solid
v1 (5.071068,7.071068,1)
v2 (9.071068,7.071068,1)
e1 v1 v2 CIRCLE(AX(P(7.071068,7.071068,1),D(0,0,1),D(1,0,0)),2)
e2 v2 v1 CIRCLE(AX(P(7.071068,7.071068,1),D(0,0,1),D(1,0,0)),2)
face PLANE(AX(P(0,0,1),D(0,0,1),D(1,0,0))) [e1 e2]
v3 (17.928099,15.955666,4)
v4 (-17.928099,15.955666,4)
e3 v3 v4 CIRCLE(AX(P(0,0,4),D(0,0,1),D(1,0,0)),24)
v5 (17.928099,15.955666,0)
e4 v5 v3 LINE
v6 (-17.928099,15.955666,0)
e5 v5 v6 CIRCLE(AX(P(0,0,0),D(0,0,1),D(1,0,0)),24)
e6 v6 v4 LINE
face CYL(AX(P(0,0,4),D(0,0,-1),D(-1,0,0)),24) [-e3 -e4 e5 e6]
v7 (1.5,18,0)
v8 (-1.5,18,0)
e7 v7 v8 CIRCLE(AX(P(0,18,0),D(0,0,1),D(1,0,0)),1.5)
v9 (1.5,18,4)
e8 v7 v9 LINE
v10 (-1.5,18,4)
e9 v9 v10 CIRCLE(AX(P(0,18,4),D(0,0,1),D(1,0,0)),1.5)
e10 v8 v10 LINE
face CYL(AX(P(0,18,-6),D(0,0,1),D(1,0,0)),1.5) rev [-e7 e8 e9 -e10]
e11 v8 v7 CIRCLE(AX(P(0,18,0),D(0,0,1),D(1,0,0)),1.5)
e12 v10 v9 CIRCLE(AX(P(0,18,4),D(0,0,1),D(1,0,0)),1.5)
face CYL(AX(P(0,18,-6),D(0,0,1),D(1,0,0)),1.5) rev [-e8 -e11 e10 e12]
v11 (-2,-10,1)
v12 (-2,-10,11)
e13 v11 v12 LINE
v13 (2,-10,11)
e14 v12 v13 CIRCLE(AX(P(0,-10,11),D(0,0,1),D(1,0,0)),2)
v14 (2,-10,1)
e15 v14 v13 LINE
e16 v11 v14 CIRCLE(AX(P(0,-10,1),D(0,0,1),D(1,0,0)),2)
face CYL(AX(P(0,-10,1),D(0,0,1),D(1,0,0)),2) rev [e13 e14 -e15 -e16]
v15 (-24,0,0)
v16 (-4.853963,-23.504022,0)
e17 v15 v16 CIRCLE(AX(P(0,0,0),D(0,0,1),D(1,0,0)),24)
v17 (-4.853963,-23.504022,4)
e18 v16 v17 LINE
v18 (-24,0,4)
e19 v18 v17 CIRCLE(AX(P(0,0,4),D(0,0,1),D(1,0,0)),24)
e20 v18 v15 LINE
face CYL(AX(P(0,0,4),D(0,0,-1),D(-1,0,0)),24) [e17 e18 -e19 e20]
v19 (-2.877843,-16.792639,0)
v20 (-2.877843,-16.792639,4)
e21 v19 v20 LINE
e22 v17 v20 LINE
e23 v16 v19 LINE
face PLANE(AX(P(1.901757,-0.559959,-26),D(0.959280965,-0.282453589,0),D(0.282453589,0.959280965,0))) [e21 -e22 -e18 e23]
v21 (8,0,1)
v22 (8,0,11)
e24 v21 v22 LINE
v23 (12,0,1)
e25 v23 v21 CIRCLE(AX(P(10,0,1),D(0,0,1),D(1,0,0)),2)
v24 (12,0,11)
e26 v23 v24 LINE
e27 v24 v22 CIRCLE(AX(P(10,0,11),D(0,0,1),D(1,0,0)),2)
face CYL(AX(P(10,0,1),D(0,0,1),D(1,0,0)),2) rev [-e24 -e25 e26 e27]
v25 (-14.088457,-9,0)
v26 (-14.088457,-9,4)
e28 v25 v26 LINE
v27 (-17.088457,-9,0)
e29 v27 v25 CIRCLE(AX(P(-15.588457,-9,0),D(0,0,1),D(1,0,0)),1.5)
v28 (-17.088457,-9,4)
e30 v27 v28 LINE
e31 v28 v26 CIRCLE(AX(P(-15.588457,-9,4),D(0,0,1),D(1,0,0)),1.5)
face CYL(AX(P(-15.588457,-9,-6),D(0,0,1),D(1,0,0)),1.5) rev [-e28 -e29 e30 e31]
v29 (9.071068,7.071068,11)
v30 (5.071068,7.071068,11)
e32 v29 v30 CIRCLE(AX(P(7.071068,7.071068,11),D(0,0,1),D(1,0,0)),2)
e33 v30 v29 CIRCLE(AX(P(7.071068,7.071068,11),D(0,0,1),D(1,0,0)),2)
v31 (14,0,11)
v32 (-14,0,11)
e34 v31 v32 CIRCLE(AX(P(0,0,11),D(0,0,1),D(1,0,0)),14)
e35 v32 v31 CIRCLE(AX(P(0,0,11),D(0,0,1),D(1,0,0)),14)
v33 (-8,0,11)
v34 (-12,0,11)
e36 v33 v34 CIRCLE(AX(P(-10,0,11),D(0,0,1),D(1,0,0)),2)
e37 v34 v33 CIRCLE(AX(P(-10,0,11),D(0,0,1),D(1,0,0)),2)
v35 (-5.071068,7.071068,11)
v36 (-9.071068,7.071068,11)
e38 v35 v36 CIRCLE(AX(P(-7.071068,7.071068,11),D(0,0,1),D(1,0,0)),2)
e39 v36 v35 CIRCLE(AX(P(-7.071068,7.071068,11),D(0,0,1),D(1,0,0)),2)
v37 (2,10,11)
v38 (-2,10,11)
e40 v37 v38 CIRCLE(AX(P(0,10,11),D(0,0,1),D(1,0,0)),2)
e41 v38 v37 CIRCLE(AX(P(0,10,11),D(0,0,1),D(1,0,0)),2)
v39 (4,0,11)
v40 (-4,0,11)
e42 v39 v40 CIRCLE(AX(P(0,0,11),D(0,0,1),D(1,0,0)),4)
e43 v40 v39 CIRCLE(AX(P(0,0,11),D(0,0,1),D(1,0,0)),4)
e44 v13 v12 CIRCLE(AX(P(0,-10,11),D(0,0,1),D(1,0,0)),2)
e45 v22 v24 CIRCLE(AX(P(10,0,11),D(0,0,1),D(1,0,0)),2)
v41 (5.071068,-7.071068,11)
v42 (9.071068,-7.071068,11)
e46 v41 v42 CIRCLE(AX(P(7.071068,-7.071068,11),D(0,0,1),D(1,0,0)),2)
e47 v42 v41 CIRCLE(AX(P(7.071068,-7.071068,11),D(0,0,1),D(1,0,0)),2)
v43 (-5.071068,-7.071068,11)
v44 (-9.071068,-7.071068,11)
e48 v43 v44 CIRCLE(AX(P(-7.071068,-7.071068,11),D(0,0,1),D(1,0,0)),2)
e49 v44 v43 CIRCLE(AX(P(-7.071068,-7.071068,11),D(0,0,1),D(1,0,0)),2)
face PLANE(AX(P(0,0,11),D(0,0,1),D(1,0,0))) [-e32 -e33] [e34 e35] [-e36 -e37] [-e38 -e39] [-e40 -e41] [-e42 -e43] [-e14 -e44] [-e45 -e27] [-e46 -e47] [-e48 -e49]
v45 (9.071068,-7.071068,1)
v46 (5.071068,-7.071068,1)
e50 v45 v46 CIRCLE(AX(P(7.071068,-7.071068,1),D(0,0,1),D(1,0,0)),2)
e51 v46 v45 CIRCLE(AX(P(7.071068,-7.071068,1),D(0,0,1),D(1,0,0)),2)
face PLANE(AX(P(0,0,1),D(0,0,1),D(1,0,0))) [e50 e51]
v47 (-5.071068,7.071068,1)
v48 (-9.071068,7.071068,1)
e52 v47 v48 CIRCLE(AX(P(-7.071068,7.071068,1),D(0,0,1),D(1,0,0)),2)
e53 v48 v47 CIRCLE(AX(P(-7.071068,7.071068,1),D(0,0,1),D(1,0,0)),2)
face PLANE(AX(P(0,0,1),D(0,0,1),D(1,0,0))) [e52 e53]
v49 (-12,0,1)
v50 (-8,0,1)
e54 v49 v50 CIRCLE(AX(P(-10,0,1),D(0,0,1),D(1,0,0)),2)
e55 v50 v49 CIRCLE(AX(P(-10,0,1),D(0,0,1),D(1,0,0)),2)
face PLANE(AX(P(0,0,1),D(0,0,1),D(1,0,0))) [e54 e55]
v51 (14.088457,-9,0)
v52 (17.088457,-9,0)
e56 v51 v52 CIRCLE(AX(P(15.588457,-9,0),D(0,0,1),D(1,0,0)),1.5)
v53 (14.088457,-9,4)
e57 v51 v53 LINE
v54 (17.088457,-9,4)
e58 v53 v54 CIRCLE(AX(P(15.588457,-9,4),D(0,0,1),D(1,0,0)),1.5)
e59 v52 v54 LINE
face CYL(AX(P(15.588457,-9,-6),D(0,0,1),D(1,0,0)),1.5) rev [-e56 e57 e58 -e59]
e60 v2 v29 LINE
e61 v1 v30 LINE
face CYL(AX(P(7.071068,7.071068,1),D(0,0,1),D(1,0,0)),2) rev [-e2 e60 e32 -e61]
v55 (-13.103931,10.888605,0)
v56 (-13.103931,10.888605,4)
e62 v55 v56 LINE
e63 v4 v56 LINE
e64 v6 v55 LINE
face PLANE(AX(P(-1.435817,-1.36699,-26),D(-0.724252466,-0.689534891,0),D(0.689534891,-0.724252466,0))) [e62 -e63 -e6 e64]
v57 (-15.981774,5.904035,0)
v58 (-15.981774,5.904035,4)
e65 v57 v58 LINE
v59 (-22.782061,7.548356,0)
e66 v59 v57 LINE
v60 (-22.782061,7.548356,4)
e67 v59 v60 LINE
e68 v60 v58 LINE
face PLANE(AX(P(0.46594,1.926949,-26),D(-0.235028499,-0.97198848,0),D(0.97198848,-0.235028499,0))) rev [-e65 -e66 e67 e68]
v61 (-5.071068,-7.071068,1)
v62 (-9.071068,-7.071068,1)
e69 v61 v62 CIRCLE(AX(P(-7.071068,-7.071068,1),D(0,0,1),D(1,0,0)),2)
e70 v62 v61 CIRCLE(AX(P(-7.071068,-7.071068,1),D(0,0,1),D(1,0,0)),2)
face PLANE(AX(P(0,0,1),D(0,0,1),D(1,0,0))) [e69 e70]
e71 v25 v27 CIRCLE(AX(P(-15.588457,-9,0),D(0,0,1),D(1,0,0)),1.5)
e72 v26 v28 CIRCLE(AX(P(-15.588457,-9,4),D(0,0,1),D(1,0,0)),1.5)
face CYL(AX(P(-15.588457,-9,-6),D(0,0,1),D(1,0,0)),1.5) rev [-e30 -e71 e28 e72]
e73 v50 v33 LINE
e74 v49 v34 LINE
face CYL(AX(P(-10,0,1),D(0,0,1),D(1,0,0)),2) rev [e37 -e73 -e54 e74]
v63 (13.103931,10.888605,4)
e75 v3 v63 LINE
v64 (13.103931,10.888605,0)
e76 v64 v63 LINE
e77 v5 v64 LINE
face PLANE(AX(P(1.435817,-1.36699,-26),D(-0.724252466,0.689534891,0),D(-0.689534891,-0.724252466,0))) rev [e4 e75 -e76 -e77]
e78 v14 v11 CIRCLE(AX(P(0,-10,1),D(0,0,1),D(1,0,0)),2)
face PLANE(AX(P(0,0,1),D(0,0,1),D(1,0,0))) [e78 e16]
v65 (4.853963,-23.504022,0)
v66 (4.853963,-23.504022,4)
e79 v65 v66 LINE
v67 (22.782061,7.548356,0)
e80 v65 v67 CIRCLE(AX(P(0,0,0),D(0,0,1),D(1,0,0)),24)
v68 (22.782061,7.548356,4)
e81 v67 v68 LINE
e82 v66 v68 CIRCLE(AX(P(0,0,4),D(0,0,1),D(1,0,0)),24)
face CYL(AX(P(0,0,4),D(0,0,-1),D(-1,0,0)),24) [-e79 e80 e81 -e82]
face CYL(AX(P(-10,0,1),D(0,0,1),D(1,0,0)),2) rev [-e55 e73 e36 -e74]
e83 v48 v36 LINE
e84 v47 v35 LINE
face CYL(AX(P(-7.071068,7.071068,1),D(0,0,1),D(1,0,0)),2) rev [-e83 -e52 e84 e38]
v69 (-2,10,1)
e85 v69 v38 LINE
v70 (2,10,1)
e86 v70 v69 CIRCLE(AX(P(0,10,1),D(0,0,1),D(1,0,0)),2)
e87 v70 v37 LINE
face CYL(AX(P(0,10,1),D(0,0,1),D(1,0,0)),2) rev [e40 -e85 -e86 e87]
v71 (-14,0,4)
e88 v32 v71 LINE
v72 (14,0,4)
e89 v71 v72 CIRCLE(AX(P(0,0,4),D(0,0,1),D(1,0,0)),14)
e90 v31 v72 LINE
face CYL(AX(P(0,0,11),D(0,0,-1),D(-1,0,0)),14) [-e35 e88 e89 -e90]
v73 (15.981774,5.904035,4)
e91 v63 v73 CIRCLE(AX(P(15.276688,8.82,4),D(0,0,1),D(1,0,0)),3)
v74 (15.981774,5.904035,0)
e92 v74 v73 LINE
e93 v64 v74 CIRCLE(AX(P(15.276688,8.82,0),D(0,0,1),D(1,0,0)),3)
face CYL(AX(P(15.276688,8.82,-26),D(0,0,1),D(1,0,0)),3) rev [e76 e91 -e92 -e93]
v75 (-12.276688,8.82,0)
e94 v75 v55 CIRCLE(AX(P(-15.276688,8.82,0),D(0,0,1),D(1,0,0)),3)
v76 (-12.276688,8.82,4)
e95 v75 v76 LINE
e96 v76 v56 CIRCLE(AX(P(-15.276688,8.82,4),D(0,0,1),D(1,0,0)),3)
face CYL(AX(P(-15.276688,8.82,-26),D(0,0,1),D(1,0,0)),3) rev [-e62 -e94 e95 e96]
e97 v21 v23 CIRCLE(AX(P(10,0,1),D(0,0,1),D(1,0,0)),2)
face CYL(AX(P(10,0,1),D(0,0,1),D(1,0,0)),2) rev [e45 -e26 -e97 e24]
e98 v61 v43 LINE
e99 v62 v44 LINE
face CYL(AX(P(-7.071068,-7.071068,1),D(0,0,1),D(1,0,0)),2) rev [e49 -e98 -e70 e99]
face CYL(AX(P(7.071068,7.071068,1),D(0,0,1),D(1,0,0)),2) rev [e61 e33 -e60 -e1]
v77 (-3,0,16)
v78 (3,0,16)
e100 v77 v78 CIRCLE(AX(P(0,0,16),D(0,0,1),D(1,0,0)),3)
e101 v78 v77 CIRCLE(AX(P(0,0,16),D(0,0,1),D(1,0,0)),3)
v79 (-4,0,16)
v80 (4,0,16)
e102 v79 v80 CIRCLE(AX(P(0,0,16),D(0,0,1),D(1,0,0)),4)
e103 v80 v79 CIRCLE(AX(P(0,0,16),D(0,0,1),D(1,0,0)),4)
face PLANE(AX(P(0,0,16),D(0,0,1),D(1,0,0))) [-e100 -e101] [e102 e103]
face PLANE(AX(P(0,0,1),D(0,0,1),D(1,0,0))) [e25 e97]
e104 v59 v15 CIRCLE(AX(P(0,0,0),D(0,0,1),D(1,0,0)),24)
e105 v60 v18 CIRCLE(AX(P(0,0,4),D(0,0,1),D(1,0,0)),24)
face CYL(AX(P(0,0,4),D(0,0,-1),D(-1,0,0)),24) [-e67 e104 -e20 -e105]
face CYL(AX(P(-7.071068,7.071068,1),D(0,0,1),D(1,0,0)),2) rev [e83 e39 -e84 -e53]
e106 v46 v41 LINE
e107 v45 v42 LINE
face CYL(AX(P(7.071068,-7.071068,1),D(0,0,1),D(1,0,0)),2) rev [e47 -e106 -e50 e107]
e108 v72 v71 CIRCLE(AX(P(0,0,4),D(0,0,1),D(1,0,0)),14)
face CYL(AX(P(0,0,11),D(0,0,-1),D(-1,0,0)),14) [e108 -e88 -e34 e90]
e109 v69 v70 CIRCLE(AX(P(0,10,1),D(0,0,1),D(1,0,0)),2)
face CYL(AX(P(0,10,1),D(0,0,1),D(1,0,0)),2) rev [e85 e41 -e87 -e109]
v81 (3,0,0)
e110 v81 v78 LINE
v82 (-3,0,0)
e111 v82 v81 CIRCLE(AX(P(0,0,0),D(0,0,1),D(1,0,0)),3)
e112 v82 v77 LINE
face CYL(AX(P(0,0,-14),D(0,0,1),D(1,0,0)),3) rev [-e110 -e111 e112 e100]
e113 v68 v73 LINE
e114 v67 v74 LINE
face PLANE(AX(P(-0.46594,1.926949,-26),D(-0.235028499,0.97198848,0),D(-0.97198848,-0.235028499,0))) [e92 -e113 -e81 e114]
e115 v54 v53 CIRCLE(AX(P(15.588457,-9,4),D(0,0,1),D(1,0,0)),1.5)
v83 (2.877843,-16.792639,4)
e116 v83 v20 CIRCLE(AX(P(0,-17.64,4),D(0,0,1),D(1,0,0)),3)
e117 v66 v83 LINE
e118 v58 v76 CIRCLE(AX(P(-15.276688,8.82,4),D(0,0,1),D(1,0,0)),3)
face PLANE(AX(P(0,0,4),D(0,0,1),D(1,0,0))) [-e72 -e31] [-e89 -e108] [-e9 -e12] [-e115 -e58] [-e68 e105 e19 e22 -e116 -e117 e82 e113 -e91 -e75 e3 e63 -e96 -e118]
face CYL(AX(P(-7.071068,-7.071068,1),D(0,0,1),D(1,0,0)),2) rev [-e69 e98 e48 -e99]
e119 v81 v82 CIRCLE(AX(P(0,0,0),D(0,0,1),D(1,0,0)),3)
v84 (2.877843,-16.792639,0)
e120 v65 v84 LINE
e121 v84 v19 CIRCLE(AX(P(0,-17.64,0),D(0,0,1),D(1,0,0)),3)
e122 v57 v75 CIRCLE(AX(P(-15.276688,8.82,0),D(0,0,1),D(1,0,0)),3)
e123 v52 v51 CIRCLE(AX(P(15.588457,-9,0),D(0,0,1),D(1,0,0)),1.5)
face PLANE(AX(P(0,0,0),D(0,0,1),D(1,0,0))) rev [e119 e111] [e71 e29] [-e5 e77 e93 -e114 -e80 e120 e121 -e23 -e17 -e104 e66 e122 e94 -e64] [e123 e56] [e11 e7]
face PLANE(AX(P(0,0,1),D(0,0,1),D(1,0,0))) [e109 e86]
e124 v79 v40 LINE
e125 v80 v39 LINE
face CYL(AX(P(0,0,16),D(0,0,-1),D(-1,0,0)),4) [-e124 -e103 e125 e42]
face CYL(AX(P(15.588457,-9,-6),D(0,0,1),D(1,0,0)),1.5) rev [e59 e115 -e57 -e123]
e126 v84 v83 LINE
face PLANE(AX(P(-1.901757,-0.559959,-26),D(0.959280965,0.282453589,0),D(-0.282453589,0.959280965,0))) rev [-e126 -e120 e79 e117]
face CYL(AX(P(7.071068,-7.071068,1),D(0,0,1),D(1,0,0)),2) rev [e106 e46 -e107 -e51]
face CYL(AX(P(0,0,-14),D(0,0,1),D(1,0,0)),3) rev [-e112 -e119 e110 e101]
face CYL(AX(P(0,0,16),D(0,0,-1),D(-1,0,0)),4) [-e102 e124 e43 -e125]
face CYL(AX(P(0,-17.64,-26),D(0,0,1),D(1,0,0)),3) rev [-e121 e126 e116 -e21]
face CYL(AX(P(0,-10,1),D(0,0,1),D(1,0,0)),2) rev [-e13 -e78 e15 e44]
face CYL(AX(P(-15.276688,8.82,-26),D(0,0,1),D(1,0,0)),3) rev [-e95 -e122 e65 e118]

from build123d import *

# Parameters (mm, degrees)
FLANGE_DISC_SKETCH_R    = 24
FLANGE_DISC_48_DEPTH    = 4
HUB_SKETCH_R            = 14
HUB_28_DEPTH            = 7
FLANGE_HOLES_SKETCH_R   = 1.5
FLANGE_HOLES_3X_3_DEPTH = 10
HUB_HOLES_SKETCH_R      = 2
HUB_HOLES_8X_4_DEPTH    = 10
CENTRE_SPIGOT_SKETCH_R  = 4
CENTRE_SPIGOT_8_DEPTH   = 5
BORE_SKETCH_R           = 3
BORE_6_DEPTH            = 30
EDGE_START              = -30
EDGE_NOTCHES_DEPTH      = 30


with BuildPart() as part:
    # Flange Disc Sketch → Flange Disc Ø48 (new body)
    with BuildSketch(Plane.XY):
        Circle(FLANGE_DISC_SKETCH_R)
    extrude(amount=FLANGE_DISC_48_DEPTH)

    # Hub Sketch → Hub Ø28 (add)
    with BuildSketch(Plane.XY.offset(4)):
        Circle(HUB_SKETCH_R)
    extrude(amount=HUB_28_DEPTH)

    # Flange Holes Sketch → Flange Holes 3xØ3 (cut)
    with BuildSketch(Plane.XY.offset(4)):
        with Locations((0, 18)):
            Circle(FLANGE_HOLES_SKETCH_R)
        with Locations((15.588457268, -9)):
            Circle(FLANGE_HOLES_SKETCH_R)
        with Locations((-15.588457268, -9)):
            Circle(FLANGE_HOLES_SKETCH_R)
    extrude(amount=-FLANGE_HOLES_3X_3_DEPTH, mode=Mode.SUBTRACT)

    # Hub Holes Sketch → Hub Holes 8xØ4 (cut)
    with BuildSketch(Plane.XY.offset(11)):
        with Locations((0, 10)):
            Circle(HUB_HOLES_SKETCH_R)
        with Locations((7.071067812, 7.071067812)):
            Circle(HUB_HOLES_SKETCH_R)
        with Locations((10, 0)):
            Circle(HUB_HOLES_SKETCH_R)
        with Locations((7.071067812, -7.071067812)):
            Circle(HUB_HOLES_SKETCH_R)
        with Locations((0, -10)):
            Circle(HUB_HOLES_SKETCH_R)
        with Locations((-7.071067812, -7.071067812)):
            Circle(HUB_HOLES_SKETCH_R)
        with Locations((-10, 0)):
            Circle(HUB_HOLES_SKETCH_R)
        with Locations((-7.071067812, 7.071067812)):
            Circle(HUB_HOLES_SKETCH_R)
    extrude(amount=-HUB_HOLES_8X_4_DEPTH, mode=Mode.SUBTRACT)

    # Centre Spigot Sketch → Centre Spigot Ø8 (add)
    with BuildSketch(Plane.XY.offset(11)):
        Circle(CENTRE_SPIGOT_SKETCH_R)
    extrude(amount=CENTRE_SPIGOT_8_DEPTH)

    # Bore Sketch → Bore Ø6 (cut)
    with BuildSketch(Plane.XY.offset(16)):
        Circle(BORE_SKETCH_R)
    extrude(amount=-BORE_6_DEPTH, mode=Mode.SUBTRACT)

    # Edge Notches Sketch → Edge Notches (cut)
    with BuildSketch(Plane.XY.offset(4).offset(EDGE_START)):
        with BuildLine():
            ThreePointArc((-17.92809871, 15.955665973), (-20.784609691, 12), (-22.782061422, 7.548355939))
            Line((-22.782061422, 7.548355939), (-16.571312466, 6.046586076))
            ThreePointArc((-16.571312466, 6.046586076), (-15.276688123, 8.82), (-13.52215338, 11.327884531))
            Line((-13.52215338, 11.327884531), (-17.92809871, 15.955665973))
        make_face()
        with BuildLine():
            ThreePointArc((-13.52215338, 11.327884531), (-15.276688123, 8.82), (-16.571312466, 6.046586076))
            Line((-16.571312466, 6.046586076), (-15.98177362, 5.904034561))
            ThreePointArc((-15.98177362, 5.904034561), (-12.678611911, 7.32), (-13.103930725, 10.888604672))
            Line((-13.103930725, 10.888604672), (-13.52215338, 11.327884531))
        make_face()
        with BuildLine():
            Line((16.571312466, 6.046586076), (22.782061422, 7.548355939))
            ThreePointArc((22.782061422, 7.548355939), (20.784609691, 12), (17.92809871, 15.955665973))
            Line((17.92809871, 15.955665973), (13.52215338, 11.327884531))
            ThreePointArc((13.52215338, 11.327884531), (15.276688123, 8.82), (16.571312466, 6.046586076))
        make_face()
        with BuildLine():
            ThreePointArc((16.571312466, 6.046586076), (15.276688123, 8.82), (13.52215338, 11.327884531))
            Line((13.52215338, 11.327884531), (13.103930725, 10.888604672))
            ThreePointArc((13.103930725, 10.888604672), (12.678611911, 7.32), (15.98177362, 5.904034561))
            Line((15.98177362, 5.904034561), (16.571312466, 6.046586076))
        make_face()
        with BuildLine():
            Line((-3.049159085, -17.374470607), (-4.853962711, -23.504021911))
            ThreePointArc((-4.853962711, -23.504021911), (0, -24), (4.853962711, -23.504021911))
            Line((4.853962711, -23.504021911), (3.049159085, -17.374470607))
            ThreePointArc((3.049159085, -17.374470607), (0, -17.64), (-3.049159085, -17.374470607))
        make_face()
        with BuildLine():
            Line((-2.877842895, -16.792639233), (-3.049159085, -17.374470607))
            ThreePointArc((-3.049159085, -17.374470607), (0, -17.64), (3.049159085, -17.374470607))
            Line((3.049159085, -17.374470607), (2.877842895, -16.792639233))
            ThreePointArc((2.877842895, -16.792639233), (0, -14.64), (-2.877842895, -16.792639233))
        make_face()
    extrude(amount=EDGE_NOTCHES_DEPTH, mode=Mode.SUBTRACT)


solid = part.part
